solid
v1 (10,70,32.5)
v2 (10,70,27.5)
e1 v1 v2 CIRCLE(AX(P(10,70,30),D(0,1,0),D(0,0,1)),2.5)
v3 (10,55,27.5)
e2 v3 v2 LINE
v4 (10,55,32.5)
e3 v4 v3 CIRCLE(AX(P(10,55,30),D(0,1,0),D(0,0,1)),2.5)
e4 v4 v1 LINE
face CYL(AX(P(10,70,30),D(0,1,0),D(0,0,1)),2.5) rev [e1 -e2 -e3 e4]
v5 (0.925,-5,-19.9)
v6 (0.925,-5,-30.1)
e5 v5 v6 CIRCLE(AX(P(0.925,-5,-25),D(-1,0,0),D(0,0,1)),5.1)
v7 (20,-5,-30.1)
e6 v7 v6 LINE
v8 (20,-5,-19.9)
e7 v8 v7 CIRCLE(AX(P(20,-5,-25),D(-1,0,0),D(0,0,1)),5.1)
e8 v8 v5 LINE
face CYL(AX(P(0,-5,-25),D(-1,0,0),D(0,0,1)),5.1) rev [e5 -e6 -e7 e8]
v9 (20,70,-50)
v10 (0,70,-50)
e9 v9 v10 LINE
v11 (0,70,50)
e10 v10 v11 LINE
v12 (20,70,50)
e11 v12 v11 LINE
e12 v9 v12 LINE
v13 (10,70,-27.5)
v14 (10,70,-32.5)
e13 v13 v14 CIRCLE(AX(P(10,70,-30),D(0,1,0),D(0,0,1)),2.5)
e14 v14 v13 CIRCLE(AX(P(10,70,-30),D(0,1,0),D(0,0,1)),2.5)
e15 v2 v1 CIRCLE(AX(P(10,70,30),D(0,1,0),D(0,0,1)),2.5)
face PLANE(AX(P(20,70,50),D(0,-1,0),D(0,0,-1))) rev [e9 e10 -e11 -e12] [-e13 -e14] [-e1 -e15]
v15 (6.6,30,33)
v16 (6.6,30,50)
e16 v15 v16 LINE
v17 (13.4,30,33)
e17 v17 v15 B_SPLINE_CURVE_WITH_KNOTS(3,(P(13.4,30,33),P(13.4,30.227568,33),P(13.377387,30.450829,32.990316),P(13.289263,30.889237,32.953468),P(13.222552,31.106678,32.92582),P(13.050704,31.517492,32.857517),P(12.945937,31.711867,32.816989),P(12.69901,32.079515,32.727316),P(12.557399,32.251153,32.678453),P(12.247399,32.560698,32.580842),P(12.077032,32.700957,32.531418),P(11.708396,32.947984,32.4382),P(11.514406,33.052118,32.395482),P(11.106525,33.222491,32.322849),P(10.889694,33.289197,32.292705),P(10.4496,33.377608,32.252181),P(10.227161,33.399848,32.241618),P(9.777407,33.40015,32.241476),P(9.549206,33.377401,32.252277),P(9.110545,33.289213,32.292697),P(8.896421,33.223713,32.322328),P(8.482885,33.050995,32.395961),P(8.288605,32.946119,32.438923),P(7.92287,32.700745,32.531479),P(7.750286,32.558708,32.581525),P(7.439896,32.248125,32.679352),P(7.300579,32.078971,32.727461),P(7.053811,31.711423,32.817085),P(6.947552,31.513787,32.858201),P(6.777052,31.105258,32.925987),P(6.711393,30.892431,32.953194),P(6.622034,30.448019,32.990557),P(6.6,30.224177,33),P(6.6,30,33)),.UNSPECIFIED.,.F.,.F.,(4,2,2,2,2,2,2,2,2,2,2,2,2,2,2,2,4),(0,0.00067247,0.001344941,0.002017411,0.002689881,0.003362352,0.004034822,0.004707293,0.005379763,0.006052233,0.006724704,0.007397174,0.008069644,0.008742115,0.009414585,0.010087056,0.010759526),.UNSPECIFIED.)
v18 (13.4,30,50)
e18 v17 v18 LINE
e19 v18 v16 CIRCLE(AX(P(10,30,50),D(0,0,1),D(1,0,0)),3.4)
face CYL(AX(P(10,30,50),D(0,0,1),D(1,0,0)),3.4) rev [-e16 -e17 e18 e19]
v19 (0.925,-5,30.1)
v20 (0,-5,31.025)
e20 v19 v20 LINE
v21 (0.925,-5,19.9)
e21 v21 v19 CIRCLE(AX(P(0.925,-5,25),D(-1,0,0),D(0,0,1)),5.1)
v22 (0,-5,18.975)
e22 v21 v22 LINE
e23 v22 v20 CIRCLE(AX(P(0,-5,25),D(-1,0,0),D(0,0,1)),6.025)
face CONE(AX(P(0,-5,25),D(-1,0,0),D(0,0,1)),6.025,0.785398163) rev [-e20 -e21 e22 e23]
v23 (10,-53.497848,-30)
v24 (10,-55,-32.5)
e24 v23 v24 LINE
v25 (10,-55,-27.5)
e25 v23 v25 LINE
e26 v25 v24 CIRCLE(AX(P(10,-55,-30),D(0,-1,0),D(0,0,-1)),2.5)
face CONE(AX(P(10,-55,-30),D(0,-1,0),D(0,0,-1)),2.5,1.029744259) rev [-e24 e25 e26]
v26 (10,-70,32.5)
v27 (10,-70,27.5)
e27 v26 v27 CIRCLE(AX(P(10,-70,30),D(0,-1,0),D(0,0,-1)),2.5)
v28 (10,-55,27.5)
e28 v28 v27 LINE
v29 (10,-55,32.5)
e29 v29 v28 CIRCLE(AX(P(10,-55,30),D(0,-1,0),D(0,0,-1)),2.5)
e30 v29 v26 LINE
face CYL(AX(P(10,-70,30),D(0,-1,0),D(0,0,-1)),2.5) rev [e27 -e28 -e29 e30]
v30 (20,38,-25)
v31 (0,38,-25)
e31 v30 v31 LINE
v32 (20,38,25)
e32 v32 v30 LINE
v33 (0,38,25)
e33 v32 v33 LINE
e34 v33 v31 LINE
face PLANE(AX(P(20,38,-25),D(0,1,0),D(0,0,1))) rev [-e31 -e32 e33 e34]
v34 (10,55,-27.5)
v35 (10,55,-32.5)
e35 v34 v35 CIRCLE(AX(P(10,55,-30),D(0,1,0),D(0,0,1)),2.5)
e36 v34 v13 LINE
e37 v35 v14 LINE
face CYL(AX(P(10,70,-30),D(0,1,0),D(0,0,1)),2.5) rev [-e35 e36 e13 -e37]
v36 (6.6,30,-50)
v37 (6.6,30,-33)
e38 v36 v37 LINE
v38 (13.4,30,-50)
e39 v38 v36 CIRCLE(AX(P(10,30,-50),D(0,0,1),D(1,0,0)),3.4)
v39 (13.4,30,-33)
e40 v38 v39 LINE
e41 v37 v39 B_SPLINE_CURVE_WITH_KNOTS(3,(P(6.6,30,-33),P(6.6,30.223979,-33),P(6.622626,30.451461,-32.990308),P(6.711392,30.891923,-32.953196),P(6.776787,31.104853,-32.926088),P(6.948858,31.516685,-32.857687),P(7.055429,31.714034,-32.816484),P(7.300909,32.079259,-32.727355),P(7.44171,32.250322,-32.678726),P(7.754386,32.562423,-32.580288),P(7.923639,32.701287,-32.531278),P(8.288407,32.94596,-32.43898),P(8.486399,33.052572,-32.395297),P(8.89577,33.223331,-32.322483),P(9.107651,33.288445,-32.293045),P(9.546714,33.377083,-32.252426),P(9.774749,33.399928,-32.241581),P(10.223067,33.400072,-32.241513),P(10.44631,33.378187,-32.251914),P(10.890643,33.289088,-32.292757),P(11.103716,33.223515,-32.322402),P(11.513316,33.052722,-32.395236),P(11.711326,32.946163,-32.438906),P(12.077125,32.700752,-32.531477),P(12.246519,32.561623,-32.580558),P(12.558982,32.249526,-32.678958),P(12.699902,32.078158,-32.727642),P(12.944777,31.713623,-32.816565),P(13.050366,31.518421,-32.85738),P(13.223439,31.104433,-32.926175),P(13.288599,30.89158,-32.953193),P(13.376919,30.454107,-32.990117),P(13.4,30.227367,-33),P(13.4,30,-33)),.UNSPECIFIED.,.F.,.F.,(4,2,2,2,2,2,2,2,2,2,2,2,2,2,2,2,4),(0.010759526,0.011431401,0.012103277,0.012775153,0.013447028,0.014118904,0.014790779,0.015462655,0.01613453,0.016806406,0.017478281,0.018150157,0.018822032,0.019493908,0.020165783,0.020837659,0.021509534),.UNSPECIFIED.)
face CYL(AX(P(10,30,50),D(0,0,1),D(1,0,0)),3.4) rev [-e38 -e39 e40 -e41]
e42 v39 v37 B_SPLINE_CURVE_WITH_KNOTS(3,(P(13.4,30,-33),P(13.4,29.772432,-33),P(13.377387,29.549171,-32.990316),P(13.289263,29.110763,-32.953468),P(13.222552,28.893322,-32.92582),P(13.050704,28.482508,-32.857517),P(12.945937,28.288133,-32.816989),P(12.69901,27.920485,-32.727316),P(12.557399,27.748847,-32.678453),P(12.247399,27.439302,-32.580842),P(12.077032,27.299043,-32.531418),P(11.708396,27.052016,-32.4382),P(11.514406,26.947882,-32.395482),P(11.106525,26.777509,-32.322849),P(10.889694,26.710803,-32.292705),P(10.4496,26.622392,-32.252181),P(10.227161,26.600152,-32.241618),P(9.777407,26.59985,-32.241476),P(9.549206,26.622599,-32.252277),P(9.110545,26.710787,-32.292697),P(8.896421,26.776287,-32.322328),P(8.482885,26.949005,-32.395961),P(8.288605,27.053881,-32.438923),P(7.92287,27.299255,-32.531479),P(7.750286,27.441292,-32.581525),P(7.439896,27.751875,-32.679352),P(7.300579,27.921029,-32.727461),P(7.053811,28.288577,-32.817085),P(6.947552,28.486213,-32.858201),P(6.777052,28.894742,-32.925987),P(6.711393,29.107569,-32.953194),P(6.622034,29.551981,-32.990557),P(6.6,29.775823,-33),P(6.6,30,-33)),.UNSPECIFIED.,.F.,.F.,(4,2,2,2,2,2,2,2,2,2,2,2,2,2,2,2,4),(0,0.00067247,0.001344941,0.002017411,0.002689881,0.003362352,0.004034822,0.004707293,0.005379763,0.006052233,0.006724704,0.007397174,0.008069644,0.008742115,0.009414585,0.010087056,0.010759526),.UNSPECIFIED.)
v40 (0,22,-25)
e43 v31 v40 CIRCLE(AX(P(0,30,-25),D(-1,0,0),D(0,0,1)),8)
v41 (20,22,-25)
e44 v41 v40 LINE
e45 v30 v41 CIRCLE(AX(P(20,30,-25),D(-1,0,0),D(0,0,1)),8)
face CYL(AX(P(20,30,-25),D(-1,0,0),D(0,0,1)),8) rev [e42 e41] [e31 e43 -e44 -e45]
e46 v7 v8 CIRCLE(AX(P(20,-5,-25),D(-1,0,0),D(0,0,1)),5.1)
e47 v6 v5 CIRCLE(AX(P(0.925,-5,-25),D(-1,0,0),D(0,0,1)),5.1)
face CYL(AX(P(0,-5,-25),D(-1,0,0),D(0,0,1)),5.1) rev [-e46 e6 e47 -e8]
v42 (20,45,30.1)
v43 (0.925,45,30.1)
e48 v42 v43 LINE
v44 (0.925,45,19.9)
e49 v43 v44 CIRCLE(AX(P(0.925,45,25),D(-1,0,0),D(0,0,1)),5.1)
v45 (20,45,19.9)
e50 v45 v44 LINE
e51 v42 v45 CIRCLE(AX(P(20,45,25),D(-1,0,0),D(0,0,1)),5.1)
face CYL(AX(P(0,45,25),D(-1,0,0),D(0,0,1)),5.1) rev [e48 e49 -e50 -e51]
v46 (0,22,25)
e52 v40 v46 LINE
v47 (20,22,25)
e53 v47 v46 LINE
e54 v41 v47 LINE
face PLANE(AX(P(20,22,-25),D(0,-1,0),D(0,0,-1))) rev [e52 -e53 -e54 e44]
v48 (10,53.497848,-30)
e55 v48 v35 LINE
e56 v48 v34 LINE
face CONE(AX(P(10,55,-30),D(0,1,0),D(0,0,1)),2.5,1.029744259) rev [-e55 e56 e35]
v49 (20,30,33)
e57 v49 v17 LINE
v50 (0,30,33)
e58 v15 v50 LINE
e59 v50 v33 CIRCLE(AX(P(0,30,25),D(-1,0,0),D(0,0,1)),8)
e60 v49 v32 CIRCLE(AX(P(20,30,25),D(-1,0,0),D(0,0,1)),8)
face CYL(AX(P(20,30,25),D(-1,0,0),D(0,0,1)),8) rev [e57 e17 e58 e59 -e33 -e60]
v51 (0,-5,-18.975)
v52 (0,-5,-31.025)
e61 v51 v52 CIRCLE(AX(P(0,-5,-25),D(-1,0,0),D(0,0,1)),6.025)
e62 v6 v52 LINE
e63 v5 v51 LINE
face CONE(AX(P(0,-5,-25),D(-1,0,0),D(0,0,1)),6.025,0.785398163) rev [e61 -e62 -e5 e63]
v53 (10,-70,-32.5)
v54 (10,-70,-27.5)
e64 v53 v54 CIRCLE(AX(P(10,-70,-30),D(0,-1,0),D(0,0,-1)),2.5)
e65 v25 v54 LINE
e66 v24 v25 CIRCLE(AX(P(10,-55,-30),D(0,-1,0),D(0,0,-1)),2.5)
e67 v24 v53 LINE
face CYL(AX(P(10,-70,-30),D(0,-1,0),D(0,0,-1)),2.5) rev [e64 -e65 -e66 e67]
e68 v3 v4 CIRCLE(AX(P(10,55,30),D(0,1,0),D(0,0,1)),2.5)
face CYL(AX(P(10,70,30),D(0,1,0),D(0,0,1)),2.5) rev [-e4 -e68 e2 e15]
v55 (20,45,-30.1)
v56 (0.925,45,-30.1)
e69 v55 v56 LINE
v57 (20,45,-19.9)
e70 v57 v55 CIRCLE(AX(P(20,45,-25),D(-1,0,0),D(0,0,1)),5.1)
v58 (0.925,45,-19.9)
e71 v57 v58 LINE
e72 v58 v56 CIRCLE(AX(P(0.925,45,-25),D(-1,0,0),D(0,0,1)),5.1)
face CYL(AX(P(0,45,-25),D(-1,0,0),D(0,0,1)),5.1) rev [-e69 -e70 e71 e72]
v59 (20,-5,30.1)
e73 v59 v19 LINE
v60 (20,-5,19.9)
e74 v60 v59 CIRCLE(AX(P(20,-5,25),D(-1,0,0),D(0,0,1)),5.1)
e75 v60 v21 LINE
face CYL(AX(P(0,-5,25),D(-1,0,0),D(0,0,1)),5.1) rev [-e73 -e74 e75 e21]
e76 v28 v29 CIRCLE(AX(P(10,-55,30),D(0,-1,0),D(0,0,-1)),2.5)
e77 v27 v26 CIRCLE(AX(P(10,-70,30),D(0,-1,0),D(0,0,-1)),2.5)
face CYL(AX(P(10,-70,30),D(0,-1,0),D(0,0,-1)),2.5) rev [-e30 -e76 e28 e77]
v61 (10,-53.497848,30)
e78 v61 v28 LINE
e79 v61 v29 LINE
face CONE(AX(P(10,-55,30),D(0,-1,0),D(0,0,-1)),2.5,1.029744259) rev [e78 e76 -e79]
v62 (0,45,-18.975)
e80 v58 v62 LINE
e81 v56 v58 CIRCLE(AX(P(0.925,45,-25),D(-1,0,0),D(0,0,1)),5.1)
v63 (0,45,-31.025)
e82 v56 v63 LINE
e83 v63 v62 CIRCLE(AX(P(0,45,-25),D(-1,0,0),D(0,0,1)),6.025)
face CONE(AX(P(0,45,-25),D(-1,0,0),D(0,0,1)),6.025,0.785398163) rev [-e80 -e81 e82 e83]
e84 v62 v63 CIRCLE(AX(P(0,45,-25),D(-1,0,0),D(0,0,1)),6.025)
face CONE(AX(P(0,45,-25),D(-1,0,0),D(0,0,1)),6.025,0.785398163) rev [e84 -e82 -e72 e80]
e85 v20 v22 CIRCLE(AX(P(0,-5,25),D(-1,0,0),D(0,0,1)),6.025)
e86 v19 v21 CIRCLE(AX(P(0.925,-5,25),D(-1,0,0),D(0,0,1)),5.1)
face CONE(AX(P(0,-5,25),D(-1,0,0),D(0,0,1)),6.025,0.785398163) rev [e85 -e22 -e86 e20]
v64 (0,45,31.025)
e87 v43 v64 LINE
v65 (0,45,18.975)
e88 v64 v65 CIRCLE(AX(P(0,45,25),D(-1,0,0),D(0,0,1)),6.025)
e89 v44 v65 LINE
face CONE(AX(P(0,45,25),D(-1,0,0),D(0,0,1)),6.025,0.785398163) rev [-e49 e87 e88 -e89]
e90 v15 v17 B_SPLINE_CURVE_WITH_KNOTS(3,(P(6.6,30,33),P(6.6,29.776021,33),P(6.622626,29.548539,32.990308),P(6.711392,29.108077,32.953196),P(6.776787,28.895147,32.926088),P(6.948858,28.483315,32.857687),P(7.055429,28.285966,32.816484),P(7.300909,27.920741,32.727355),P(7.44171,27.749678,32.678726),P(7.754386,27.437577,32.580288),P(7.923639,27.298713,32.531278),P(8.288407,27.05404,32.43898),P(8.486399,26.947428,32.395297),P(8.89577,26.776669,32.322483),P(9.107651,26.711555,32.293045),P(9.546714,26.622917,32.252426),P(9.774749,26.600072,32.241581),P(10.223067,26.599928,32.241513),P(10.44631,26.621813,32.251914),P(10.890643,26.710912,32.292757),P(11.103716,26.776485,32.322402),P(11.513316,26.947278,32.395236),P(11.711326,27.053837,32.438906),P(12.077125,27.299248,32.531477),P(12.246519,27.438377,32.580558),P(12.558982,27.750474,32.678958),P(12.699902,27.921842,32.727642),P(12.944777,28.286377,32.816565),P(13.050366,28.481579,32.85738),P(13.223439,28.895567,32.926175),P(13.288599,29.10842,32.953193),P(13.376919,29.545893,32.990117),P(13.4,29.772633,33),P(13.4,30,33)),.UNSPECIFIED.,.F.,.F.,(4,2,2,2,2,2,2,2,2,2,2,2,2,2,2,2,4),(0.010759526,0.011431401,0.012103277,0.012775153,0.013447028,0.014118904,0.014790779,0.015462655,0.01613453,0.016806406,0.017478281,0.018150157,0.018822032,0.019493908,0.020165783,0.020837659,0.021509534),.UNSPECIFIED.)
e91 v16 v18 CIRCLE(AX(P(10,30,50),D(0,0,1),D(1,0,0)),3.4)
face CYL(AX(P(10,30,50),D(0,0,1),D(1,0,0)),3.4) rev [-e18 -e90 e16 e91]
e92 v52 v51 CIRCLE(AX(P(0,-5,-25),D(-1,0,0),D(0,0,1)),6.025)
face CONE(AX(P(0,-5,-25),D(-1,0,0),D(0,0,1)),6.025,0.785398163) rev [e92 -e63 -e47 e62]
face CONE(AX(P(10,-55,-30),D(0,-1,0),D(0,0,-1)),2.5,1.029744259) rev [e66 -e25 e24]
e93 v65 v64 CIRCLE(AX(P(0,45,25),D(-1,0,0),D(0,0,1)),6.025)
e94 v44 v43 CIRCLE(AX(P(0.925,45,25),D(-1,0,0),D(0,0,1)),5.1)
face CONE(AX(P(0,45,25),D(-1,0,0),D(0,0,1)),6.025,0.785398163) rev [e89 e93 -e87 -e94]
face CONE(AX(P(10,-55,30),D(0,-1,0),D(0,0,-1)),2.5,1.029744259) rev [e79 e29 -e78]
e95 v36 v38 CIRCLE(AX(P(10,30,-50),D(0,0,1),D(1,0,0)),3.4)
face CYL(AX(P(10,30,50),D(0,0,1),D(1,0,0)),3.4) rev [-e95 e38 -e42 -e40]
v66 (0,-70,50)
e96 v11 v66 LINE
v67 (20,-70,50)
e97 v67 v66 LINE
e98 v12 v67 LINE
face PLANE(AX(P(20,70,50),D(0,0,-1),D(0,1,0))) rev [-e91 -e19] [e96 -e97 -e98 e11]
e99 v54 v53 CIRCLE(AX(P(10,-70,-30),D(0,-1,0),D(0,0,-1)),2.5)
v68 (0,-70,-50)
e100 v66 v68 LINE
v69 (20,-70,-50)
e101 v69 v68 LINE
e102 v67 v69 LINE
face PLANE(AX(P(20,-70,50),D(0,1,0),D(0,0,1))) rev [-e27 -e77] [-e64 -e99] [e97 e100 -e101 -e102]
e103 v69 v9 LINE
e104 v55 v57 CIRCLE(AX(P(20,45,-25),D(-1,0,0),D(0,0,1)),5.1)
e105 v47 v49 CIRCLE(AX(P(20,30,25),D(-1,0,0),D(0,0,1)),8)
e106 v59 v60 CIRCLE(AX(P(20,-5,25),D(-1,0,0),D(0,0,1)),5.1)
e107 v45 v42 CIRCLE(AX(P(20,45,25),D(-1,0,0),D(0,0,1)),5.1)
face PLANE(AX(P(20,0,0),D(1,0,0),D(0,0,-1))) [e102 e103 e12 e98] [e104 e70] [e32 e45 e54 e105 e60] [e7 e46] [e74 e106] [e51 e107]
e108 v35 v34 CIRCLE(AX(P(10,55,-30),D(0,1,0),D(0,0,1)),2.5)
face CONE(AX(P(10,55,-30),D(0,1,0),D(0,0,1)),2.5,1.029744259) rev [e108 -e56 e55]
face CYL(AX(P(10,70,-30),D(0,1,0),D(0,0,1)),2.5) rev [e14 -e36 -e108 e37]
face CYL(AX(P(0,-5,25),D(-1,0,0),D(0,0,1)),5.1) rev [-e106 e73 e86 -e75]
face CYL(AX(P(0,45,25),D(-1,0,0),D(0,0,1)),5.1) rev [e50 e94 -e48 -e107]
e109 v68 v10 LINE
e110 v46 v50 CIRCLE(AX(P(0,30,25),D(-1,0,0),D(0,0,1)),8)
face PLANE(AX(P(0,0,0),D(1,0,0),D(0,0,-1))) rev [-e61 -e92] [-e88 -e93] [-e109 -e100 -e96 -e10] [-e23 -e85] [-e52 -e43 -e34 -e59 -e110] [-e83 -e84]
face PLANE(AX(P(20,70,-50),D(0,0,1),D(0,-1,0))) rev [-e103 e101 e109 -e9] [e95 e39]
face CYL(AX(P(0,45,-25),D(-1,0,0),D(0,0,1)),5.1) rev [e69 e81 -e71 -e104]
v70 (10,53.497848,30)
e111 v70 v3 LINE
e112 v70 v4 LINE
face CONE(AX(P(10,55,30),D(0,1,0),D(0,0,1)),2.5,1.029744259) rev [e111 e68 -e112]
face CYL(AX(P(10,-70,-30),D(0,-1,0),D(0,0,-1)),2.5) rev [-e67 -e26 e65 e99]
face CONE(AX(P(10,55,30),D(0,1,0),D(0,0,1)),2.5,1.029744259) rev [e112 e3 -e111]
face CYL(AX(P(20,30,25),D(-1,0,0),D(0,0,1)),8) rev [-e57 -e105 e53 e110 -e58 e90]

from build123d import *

# Parameters (mm, degrees)
SKETCH_1_W                    = 100
SKETCH_1_H                    = 140
EXTRUDE_1_DEPTH               = 20
HOLE_WIZARD_M6_1_D            = 5
HOLE_WIZARD_M6_1_DEPTH        = 15
HOLE_WIZARD_M6_1_TIP          = 1.502151548
CUT_EXTRUDE_1_DEPTH           = 89.317608663
HOLE_WIZARD_M8_1_D            = 6.8
HOLE_WIZARD_M12_1_D           = 10.2
HOLE_WIZARD_M12_1_CSINK_D     = 12.05
HOLE_WIZARD_M12_1_CSINK_ANGLE = 90
HOLE_WIZARD_M6_2_D            = 5
HOLE_WIZARD_M6_2_DEPTH        = 15
HOLE_WIZARD_M6_2_TIP          = 1.502151548


with BuildPart() as part:
    # 草图1 → 凸台-拉伸1 (new body)
    with BuildSketch(Plane(origin=(0, 0, 0), x_dir=(0, 0, -1), z_dir=(1, 0, 0))):
        Rectangle(SKETCH_1_W, SKETCH_1_H)
    extrude(amount=EXTRUDE_1_DEPTH)

    # M6 螺纹孔1
    with Locations(Plane(origin=(0, -70, 0), x_dir=(-1, 0, 0), z_dir=(0, -1, 0))):
        with Locations((-10, 30), (-10, -30)):
            Hole(HOLE_WIZARD_M6_1_D / 2, depth=HOLE_WIZARD_M6_1_DEPTH)
            with Locations((0, 0, -(HOLE_WIZARD_M6_1_DEPTH + HOLE_WIZARD_M6_1_TIP / 2))):  # 118° drill point
                Cone(0, HOLE_WIZARD_M6_1_D / 2, HOLE_WIZARD_M6_1_TIP, mode=Mode.SUBTRACT)

    # 草图4 → 切除-拉伸1 (cut, through all)
    with BuildSketch(Plane.ZY):
        with BuildLine():
            Line((-25, 38), (25, 38))
            ThreePointArc((25, 38), (33, 30), (25, 22))
            Line((25, 22), (-25, 22))
            ThreePointArc((-25, 22), (-33, 30), (-25, 38))
        make_face()
    extrude(amount=-CUT_EXTRUDE_1_DEPTH, mode=Mode.SUBTRACT)

    # M8 螺纹孔1 (through all)
    with Locations(Plane.XY.offset(50)):
        with Locations((10, 30)):
            Hole(HOLE_WIZARD_M8_1_D / 2)

    # M12 螺纹孔1 (through all)
    with Locations(Plane.ZY):
        with Locations((-25, 45), (25, 45), (-25, -5), (25, -5)):
            CounterSinkHole(HOLE_WIZARD_M12_1_D / 2, HOLE_WIZARD_M12_1_CSINK_D / 2, counter_sink_angle=HOLE_WIZARD_M12_1_CSINK_ANGLE)

    # M6 螺纹孔2
    with Locations(Plane(origin=(0, 70, 0), x_dir=(1, 0, 0), z_dir=(0, 1, 0))):
        with Locations((10, 30), (10, -30)):
            Hole(HOLE_WIZARD_M6_2_D / 2, depth=HOLE_WIZARD_M6_2_DEPTH)
            with Locations((0, 0, -(HOLE_WIZARD_M6_2_DEPTH + HOLE_WIZARD_M6_2_TIP / 2))):  # 118° drill point
                Cone(0, HOLE_WIZARD_M6_2_D / 2, HOLE_WIZARD_M6_2_TIP, mode=Mode.SUBTRACT)


solid = part.part
